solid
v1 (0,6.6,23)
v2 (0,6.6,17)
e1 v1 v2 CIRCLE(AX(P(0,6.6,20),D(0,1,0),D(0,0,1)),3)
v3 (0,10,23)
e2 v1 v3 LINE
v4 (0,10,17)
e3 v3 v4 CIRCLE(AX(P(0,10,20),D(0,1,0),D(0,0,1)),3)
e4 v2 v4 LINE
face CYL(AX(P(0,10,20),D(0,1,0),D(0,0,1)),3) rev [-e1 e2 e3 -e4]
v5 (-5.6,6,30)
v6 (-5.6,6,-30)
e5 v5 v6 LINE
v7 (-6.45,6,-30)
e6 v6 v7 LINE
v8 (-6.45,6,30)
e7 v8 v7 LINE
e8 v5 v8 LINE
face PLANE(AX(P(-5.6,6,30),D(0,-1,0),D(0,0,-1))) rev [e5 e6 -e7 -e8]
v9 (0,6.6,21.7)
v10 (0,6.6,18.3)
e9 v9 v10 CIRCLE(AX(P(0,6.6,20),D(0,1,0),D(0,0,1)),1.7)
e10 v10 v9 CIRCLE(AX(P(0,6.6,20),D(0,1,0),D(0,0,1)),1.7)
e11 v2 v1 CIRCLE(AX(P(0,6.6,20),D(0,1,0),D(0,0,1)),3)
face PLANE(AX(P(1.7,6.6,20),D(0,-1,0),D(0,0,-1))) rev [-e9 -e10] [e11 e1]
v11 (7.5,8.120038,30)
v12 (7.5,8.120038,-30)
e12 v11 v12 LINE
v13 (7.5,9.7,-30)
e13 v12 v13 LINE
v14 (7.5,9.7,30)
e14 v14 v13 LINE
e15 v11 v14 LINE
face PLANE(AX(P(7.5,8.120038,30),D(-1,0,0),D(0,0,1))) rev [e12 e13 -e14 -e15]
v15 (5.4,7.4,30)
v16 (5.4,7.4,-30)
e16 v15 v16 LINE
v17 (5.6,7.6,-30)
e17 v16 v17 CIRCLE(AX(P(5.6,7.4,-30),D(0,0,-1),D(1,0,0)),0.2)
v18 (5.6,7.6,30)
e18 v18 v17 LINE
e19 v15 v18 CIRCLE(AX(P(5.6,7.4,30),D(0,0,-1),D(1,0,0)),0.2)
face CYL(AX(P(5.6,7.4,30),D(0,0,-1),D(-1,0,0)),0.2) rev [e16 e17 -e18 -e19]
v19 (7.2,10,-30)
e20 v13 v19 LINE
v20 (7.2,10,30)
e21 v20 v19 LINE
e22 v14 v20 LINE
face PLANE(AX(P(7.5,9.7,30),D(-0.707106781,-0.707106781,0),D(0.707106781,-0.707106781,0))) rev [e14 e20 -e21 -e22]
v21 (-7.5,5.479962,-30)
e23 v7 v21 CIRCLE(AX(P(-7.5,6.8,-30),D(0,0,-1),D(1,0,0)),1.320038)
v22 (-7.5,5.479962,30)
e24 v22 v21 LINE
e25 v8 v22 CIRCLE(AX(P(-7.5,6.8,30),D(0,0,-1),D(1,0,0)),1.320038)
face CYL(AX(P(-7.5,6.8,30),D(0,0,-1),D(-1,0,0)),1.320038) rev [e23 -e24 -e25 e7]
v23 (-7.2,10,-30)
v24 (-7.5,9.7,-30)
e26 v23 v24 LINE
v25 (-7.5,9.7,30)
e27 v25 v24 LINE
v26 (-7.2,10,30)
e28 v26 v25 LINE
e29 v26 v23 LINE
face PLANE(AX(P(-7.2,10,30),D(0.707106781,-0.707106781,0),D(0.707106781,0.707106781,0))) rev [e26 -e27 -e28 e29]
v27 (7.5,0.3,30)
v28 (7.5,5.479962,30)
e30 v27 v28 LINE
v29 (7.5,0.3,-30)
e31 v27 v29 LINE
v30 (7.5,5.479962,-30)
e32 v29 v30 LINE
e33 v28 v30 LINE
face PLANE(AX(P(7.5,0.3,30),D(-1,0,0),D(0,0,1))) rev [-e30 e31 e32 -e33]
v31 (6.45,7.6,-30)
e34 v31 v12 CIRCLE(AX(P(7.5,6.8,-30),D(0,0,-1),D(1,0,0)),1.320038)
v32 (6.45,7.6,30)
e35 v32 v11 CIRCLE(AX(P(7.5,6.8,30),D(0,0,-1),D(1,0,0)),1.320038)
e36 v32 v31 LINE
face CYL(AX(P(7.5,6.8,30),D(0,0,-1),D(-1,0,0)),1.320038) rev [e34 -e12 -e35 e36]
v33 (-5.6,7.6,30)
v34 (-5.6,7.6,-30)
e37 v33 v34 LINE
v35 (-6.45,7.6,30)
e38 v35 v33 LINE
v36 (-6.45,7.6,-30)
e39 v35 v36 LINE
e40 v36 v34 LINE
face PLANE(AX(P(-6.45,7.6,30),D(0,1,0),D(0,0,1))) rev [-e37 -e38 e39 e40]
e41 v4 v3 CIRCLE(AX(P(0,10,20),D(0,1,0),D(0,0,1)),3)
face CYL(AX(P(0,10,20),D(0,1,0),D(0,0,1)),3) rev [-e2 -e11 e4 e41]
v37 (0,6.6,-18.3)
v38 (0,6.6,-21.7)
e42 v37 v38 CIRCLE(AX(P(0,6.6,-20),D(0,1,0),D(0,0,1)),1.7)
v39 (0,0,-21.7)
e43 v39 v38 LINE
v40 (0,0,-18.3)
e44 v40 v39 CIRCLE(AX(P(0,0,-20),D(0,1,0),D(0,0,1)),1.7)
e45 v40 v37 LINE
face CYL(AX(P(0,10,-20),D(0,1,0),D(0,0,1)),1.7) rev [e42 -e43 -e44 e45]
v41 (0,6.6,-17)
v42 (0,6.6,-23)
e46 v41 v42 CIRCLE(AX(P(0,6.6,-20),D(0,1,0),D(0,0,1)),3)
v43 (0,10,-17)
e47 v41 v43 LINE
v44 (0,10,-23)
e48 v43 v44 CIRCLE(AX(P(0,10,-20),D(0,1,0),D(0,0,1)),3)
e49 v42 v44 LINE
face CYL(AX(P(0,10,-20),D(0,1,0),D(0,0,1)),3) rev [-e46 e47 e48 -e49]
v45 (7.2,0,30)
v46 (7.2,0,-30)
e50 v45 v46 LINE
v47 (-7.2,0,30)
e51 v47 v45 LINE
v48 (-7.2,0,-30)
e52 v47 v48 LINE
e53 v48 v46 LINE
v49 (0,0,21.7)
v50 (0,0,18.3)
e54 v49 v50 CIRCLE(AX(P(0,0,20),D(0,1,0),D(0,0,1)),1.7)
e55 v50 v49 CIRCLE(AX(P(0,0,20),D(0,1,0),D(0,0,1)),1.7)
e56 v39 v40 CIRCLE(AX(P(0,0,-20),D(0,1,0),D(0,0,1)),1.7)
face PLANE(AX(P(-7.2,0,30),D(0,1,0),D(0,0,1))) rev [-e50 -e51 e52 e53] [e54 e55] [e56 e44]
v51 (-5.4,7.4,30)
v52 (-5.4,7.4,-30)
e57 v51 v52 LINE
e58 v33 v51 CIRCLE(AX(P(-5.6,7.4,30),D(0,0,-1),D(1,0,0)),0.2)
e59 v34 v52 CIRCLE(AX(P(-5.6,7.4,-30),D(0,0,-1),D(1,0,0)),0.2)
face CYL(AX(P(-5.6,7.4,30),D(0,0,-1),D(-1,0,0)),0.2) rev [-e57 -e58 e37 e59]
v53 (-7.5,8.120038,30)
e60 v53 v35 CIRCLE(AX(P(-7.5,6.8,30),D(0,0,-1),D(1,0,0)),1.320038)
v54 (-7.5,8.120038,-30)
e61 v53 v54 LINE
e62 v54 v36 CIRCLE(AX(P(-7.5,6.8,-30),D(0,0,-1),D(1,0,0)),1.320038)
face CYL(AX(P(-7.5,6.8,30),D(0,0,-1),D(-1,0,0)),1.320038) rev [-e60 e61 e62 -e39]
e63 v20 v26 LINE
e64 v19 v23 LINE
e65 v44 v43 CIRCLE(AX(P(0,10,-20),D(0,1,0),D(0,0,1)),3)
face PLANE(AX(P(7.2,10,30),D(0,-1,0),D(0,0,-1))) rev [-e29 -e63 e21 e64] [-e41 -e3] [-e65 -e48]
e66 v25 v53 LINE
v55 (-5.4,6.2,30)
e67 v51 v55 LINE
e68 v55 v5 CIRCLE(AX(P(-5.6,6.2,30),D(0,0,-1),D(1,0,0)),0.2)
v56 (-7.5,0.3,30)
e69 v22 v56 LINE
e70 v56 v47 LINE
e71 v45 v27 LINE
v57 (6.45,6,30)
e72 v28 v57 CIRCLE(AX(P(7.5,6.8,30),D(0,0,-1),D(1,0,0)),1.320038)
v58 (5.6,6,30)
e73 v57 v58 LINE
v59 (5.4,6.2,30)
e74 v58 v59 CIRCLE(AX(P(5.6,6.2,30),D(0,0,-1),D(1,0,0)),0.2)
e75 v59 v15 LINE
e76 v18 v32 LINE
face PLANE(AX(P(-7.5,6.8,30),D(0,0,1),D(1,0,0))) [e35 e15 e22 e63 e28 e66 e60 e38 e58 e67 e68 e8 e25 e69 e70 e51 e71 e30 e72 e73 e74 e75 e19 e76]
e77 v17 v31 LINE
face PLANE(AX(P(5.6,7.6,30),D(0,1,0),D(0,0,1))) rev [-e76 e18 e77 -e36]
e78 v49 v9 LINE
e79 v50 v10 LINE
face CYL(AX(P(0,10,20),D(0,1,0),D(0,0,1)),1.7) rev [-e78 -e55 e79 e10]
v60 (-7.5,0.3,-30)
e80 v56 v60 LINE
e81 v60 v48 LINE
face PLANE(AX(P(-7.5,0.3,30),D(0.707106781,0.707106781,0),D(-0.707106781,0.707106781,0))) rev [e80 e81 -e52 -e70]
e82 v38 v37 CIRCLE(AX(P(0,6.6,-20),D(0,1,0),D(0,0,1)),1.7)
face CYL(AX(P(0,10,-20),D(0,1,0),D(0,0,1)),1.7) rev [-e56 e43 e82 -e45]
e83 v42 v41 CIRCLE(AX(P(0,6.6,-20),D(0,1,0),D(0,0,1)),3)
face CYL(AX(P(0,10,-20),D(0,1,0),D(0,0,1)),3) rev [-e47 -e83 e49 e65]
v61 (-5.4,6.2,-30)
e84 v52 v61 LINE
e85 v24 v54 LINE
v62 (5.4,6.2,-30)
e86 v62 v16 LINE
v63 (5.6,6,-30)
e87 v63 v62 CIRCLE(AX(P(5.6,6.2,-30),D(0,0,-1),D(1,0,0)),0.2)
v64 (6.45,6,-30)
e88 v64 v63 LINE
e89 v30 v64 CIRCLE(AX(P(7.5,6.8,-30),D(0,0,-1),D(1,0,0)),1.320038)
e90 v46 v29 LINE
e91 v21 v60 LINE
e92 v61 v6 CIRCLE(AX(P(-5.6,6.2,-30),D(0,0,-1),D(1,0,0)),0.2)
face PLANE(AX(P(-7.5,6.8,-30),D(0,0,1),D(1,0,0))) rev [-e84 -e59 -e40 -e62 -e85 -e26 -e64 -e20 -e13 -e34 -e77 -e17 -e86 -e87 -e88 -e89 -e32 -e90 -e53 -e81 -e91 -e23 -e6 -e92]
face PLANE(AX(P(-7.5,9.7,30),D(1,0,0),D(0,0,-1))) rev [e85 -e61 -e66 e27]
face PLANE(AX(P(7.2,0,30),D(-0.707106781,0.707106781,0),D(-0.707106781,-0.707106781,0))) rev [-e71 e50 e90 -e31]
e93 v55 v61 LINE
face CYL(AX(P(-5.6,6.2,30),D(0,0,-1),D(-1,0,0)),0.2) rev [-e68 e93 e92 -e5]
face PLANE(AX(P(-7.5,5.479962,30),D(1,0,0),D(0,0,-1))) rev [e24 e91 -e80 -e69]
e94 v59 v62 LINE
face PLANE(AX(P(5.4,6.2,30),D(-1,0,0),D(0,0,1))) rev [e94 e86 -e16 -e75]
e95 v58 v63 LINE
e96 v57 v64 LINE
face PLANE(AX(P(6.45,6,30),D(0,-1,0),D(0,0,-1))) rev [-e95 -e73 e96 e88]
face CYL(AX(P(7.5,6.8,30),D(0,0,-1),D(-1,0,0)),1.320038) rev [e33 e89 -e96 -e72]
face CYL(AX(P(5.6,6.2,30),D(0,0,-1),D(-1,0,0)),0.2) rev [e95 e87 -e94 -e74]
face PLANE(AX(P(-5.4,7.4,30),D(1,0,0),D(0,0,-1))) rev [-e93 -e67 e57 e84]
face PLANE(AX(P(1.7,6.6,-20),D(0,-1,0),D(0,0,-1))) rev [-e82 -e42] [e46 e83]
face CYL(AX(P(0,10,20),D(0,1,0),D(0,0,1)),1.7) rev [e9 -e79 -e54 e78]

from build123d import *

# Parameters (mm, degrees)
EXTRUDE_1_DEPTH           = 30
HOLE_WIZARD_1_D           = 3.4
HOLE_WIZARD_1_CBORE_D     = 6
HOLE_WIZARD_1_CBORE_DEPTH = 3.4
PATTERN_LINEAR_1_COUNT    = 2
PATTERN_LINEAR_1_PITCH    = 40


with BuildPart() as part:
    # 草图2 → 凸台-拉伸1 (new, symmetric)
    with BuildSketch(Plane.XY):
        with BuildLine():
            Line((7.5, 9.7), (7.2, 10))
            Line((7.2, 10), (-7.2, 10))
            Line((-7.2, 10), (-7.5, 9.7))
            Line((-7.5, 9.7), (-7.5, 8.120037878))
            ThreePointArc((-7.5, 8.120037878), (-6.914137517, 7.982905386), (-6.45, 7.6))
            Line((-6.45, 7.6), (-5.6, 7.6))
            ThreePointArc((-5.6, 7.6), (-5.458578644, 7.541421356), (-5.4, 7.4))
            Line((-5.4, 7.4), (-5.4, 6.2))
            ThreePointArc((-5.4, 6.2), (-5.458578644, 6.058578644), (-5.6, 6))
            Line((-5.6, 6), (-6.45, 6))
            ThreePointArc((-6.45, 6), (-6.914137517, 5.617094614), (-7.5, 5.479962122))
            Line((-7.5, 5.479962122), (-7.5, 0.3))
            Line((-7.5, 0.3), (-7.2, 0))
            Line((-7.2, 0), (7.2, 0))
            Line((7.2, 0), (7.5, 0.3))
            Line((7.5, 0.3), (7.5, 5.479962122))
            ThreePointArc((7.5, 5.479962122), (6.914137517, 5.617094614), (6.45, 6))
            Line((6.45, 6), (5.6, 6))
            ThreePointArc((5.6, 6), (5.458578644, 6.058578644), (5.4, 6.2))
            Line((5.4, 6.2), (5.4, 7.4))
            ThreePointArc((5.4, 7.4), (5.458578644, 7.541421356), (5.6, 7.6))
            Line((5.6, 7.6), (6.45, 7.6))
            ThreePointArc((6.45, 7.6), (6.914137517, 7.982905386), (7.5, 8.120037878))
            Line((7.5, 8.120037878), (7.5, 9.7))
        make_face()
    extrude(amount=EXTRUDE_1_DEPTH, both=True)

    # 打孔尺寸(%根据)内六角圆柱头螺钉的类型1 (through all)
    with Locations(Plane(origin=(0, 10, 20), x_dir=(0, 0, 1), z_dir=(0, 1, 0))):
        with Locations((0, 0)):
            hole_wizard_1 = CounterBoreHole(HOLE_WIZARD_1_D / 2, HOLE_WIZARD_1_CBORE_D / 2, HOLE_WIZARD_1_CBORE_DEPTH)

    # 阵列(线性)1: 打孔尺寸(%根据)内六角圆柱头螺钉的类型1 ×2
    with Locations(*[(0, 0, -i * PATTERN_LINEAR_1_PITCH) for i in range(1, PATTERN_LINEAR_1_COUNT)]):
        add(hole_wizard_1, mode=Mode.SUBTRACT)


solid = part.part
